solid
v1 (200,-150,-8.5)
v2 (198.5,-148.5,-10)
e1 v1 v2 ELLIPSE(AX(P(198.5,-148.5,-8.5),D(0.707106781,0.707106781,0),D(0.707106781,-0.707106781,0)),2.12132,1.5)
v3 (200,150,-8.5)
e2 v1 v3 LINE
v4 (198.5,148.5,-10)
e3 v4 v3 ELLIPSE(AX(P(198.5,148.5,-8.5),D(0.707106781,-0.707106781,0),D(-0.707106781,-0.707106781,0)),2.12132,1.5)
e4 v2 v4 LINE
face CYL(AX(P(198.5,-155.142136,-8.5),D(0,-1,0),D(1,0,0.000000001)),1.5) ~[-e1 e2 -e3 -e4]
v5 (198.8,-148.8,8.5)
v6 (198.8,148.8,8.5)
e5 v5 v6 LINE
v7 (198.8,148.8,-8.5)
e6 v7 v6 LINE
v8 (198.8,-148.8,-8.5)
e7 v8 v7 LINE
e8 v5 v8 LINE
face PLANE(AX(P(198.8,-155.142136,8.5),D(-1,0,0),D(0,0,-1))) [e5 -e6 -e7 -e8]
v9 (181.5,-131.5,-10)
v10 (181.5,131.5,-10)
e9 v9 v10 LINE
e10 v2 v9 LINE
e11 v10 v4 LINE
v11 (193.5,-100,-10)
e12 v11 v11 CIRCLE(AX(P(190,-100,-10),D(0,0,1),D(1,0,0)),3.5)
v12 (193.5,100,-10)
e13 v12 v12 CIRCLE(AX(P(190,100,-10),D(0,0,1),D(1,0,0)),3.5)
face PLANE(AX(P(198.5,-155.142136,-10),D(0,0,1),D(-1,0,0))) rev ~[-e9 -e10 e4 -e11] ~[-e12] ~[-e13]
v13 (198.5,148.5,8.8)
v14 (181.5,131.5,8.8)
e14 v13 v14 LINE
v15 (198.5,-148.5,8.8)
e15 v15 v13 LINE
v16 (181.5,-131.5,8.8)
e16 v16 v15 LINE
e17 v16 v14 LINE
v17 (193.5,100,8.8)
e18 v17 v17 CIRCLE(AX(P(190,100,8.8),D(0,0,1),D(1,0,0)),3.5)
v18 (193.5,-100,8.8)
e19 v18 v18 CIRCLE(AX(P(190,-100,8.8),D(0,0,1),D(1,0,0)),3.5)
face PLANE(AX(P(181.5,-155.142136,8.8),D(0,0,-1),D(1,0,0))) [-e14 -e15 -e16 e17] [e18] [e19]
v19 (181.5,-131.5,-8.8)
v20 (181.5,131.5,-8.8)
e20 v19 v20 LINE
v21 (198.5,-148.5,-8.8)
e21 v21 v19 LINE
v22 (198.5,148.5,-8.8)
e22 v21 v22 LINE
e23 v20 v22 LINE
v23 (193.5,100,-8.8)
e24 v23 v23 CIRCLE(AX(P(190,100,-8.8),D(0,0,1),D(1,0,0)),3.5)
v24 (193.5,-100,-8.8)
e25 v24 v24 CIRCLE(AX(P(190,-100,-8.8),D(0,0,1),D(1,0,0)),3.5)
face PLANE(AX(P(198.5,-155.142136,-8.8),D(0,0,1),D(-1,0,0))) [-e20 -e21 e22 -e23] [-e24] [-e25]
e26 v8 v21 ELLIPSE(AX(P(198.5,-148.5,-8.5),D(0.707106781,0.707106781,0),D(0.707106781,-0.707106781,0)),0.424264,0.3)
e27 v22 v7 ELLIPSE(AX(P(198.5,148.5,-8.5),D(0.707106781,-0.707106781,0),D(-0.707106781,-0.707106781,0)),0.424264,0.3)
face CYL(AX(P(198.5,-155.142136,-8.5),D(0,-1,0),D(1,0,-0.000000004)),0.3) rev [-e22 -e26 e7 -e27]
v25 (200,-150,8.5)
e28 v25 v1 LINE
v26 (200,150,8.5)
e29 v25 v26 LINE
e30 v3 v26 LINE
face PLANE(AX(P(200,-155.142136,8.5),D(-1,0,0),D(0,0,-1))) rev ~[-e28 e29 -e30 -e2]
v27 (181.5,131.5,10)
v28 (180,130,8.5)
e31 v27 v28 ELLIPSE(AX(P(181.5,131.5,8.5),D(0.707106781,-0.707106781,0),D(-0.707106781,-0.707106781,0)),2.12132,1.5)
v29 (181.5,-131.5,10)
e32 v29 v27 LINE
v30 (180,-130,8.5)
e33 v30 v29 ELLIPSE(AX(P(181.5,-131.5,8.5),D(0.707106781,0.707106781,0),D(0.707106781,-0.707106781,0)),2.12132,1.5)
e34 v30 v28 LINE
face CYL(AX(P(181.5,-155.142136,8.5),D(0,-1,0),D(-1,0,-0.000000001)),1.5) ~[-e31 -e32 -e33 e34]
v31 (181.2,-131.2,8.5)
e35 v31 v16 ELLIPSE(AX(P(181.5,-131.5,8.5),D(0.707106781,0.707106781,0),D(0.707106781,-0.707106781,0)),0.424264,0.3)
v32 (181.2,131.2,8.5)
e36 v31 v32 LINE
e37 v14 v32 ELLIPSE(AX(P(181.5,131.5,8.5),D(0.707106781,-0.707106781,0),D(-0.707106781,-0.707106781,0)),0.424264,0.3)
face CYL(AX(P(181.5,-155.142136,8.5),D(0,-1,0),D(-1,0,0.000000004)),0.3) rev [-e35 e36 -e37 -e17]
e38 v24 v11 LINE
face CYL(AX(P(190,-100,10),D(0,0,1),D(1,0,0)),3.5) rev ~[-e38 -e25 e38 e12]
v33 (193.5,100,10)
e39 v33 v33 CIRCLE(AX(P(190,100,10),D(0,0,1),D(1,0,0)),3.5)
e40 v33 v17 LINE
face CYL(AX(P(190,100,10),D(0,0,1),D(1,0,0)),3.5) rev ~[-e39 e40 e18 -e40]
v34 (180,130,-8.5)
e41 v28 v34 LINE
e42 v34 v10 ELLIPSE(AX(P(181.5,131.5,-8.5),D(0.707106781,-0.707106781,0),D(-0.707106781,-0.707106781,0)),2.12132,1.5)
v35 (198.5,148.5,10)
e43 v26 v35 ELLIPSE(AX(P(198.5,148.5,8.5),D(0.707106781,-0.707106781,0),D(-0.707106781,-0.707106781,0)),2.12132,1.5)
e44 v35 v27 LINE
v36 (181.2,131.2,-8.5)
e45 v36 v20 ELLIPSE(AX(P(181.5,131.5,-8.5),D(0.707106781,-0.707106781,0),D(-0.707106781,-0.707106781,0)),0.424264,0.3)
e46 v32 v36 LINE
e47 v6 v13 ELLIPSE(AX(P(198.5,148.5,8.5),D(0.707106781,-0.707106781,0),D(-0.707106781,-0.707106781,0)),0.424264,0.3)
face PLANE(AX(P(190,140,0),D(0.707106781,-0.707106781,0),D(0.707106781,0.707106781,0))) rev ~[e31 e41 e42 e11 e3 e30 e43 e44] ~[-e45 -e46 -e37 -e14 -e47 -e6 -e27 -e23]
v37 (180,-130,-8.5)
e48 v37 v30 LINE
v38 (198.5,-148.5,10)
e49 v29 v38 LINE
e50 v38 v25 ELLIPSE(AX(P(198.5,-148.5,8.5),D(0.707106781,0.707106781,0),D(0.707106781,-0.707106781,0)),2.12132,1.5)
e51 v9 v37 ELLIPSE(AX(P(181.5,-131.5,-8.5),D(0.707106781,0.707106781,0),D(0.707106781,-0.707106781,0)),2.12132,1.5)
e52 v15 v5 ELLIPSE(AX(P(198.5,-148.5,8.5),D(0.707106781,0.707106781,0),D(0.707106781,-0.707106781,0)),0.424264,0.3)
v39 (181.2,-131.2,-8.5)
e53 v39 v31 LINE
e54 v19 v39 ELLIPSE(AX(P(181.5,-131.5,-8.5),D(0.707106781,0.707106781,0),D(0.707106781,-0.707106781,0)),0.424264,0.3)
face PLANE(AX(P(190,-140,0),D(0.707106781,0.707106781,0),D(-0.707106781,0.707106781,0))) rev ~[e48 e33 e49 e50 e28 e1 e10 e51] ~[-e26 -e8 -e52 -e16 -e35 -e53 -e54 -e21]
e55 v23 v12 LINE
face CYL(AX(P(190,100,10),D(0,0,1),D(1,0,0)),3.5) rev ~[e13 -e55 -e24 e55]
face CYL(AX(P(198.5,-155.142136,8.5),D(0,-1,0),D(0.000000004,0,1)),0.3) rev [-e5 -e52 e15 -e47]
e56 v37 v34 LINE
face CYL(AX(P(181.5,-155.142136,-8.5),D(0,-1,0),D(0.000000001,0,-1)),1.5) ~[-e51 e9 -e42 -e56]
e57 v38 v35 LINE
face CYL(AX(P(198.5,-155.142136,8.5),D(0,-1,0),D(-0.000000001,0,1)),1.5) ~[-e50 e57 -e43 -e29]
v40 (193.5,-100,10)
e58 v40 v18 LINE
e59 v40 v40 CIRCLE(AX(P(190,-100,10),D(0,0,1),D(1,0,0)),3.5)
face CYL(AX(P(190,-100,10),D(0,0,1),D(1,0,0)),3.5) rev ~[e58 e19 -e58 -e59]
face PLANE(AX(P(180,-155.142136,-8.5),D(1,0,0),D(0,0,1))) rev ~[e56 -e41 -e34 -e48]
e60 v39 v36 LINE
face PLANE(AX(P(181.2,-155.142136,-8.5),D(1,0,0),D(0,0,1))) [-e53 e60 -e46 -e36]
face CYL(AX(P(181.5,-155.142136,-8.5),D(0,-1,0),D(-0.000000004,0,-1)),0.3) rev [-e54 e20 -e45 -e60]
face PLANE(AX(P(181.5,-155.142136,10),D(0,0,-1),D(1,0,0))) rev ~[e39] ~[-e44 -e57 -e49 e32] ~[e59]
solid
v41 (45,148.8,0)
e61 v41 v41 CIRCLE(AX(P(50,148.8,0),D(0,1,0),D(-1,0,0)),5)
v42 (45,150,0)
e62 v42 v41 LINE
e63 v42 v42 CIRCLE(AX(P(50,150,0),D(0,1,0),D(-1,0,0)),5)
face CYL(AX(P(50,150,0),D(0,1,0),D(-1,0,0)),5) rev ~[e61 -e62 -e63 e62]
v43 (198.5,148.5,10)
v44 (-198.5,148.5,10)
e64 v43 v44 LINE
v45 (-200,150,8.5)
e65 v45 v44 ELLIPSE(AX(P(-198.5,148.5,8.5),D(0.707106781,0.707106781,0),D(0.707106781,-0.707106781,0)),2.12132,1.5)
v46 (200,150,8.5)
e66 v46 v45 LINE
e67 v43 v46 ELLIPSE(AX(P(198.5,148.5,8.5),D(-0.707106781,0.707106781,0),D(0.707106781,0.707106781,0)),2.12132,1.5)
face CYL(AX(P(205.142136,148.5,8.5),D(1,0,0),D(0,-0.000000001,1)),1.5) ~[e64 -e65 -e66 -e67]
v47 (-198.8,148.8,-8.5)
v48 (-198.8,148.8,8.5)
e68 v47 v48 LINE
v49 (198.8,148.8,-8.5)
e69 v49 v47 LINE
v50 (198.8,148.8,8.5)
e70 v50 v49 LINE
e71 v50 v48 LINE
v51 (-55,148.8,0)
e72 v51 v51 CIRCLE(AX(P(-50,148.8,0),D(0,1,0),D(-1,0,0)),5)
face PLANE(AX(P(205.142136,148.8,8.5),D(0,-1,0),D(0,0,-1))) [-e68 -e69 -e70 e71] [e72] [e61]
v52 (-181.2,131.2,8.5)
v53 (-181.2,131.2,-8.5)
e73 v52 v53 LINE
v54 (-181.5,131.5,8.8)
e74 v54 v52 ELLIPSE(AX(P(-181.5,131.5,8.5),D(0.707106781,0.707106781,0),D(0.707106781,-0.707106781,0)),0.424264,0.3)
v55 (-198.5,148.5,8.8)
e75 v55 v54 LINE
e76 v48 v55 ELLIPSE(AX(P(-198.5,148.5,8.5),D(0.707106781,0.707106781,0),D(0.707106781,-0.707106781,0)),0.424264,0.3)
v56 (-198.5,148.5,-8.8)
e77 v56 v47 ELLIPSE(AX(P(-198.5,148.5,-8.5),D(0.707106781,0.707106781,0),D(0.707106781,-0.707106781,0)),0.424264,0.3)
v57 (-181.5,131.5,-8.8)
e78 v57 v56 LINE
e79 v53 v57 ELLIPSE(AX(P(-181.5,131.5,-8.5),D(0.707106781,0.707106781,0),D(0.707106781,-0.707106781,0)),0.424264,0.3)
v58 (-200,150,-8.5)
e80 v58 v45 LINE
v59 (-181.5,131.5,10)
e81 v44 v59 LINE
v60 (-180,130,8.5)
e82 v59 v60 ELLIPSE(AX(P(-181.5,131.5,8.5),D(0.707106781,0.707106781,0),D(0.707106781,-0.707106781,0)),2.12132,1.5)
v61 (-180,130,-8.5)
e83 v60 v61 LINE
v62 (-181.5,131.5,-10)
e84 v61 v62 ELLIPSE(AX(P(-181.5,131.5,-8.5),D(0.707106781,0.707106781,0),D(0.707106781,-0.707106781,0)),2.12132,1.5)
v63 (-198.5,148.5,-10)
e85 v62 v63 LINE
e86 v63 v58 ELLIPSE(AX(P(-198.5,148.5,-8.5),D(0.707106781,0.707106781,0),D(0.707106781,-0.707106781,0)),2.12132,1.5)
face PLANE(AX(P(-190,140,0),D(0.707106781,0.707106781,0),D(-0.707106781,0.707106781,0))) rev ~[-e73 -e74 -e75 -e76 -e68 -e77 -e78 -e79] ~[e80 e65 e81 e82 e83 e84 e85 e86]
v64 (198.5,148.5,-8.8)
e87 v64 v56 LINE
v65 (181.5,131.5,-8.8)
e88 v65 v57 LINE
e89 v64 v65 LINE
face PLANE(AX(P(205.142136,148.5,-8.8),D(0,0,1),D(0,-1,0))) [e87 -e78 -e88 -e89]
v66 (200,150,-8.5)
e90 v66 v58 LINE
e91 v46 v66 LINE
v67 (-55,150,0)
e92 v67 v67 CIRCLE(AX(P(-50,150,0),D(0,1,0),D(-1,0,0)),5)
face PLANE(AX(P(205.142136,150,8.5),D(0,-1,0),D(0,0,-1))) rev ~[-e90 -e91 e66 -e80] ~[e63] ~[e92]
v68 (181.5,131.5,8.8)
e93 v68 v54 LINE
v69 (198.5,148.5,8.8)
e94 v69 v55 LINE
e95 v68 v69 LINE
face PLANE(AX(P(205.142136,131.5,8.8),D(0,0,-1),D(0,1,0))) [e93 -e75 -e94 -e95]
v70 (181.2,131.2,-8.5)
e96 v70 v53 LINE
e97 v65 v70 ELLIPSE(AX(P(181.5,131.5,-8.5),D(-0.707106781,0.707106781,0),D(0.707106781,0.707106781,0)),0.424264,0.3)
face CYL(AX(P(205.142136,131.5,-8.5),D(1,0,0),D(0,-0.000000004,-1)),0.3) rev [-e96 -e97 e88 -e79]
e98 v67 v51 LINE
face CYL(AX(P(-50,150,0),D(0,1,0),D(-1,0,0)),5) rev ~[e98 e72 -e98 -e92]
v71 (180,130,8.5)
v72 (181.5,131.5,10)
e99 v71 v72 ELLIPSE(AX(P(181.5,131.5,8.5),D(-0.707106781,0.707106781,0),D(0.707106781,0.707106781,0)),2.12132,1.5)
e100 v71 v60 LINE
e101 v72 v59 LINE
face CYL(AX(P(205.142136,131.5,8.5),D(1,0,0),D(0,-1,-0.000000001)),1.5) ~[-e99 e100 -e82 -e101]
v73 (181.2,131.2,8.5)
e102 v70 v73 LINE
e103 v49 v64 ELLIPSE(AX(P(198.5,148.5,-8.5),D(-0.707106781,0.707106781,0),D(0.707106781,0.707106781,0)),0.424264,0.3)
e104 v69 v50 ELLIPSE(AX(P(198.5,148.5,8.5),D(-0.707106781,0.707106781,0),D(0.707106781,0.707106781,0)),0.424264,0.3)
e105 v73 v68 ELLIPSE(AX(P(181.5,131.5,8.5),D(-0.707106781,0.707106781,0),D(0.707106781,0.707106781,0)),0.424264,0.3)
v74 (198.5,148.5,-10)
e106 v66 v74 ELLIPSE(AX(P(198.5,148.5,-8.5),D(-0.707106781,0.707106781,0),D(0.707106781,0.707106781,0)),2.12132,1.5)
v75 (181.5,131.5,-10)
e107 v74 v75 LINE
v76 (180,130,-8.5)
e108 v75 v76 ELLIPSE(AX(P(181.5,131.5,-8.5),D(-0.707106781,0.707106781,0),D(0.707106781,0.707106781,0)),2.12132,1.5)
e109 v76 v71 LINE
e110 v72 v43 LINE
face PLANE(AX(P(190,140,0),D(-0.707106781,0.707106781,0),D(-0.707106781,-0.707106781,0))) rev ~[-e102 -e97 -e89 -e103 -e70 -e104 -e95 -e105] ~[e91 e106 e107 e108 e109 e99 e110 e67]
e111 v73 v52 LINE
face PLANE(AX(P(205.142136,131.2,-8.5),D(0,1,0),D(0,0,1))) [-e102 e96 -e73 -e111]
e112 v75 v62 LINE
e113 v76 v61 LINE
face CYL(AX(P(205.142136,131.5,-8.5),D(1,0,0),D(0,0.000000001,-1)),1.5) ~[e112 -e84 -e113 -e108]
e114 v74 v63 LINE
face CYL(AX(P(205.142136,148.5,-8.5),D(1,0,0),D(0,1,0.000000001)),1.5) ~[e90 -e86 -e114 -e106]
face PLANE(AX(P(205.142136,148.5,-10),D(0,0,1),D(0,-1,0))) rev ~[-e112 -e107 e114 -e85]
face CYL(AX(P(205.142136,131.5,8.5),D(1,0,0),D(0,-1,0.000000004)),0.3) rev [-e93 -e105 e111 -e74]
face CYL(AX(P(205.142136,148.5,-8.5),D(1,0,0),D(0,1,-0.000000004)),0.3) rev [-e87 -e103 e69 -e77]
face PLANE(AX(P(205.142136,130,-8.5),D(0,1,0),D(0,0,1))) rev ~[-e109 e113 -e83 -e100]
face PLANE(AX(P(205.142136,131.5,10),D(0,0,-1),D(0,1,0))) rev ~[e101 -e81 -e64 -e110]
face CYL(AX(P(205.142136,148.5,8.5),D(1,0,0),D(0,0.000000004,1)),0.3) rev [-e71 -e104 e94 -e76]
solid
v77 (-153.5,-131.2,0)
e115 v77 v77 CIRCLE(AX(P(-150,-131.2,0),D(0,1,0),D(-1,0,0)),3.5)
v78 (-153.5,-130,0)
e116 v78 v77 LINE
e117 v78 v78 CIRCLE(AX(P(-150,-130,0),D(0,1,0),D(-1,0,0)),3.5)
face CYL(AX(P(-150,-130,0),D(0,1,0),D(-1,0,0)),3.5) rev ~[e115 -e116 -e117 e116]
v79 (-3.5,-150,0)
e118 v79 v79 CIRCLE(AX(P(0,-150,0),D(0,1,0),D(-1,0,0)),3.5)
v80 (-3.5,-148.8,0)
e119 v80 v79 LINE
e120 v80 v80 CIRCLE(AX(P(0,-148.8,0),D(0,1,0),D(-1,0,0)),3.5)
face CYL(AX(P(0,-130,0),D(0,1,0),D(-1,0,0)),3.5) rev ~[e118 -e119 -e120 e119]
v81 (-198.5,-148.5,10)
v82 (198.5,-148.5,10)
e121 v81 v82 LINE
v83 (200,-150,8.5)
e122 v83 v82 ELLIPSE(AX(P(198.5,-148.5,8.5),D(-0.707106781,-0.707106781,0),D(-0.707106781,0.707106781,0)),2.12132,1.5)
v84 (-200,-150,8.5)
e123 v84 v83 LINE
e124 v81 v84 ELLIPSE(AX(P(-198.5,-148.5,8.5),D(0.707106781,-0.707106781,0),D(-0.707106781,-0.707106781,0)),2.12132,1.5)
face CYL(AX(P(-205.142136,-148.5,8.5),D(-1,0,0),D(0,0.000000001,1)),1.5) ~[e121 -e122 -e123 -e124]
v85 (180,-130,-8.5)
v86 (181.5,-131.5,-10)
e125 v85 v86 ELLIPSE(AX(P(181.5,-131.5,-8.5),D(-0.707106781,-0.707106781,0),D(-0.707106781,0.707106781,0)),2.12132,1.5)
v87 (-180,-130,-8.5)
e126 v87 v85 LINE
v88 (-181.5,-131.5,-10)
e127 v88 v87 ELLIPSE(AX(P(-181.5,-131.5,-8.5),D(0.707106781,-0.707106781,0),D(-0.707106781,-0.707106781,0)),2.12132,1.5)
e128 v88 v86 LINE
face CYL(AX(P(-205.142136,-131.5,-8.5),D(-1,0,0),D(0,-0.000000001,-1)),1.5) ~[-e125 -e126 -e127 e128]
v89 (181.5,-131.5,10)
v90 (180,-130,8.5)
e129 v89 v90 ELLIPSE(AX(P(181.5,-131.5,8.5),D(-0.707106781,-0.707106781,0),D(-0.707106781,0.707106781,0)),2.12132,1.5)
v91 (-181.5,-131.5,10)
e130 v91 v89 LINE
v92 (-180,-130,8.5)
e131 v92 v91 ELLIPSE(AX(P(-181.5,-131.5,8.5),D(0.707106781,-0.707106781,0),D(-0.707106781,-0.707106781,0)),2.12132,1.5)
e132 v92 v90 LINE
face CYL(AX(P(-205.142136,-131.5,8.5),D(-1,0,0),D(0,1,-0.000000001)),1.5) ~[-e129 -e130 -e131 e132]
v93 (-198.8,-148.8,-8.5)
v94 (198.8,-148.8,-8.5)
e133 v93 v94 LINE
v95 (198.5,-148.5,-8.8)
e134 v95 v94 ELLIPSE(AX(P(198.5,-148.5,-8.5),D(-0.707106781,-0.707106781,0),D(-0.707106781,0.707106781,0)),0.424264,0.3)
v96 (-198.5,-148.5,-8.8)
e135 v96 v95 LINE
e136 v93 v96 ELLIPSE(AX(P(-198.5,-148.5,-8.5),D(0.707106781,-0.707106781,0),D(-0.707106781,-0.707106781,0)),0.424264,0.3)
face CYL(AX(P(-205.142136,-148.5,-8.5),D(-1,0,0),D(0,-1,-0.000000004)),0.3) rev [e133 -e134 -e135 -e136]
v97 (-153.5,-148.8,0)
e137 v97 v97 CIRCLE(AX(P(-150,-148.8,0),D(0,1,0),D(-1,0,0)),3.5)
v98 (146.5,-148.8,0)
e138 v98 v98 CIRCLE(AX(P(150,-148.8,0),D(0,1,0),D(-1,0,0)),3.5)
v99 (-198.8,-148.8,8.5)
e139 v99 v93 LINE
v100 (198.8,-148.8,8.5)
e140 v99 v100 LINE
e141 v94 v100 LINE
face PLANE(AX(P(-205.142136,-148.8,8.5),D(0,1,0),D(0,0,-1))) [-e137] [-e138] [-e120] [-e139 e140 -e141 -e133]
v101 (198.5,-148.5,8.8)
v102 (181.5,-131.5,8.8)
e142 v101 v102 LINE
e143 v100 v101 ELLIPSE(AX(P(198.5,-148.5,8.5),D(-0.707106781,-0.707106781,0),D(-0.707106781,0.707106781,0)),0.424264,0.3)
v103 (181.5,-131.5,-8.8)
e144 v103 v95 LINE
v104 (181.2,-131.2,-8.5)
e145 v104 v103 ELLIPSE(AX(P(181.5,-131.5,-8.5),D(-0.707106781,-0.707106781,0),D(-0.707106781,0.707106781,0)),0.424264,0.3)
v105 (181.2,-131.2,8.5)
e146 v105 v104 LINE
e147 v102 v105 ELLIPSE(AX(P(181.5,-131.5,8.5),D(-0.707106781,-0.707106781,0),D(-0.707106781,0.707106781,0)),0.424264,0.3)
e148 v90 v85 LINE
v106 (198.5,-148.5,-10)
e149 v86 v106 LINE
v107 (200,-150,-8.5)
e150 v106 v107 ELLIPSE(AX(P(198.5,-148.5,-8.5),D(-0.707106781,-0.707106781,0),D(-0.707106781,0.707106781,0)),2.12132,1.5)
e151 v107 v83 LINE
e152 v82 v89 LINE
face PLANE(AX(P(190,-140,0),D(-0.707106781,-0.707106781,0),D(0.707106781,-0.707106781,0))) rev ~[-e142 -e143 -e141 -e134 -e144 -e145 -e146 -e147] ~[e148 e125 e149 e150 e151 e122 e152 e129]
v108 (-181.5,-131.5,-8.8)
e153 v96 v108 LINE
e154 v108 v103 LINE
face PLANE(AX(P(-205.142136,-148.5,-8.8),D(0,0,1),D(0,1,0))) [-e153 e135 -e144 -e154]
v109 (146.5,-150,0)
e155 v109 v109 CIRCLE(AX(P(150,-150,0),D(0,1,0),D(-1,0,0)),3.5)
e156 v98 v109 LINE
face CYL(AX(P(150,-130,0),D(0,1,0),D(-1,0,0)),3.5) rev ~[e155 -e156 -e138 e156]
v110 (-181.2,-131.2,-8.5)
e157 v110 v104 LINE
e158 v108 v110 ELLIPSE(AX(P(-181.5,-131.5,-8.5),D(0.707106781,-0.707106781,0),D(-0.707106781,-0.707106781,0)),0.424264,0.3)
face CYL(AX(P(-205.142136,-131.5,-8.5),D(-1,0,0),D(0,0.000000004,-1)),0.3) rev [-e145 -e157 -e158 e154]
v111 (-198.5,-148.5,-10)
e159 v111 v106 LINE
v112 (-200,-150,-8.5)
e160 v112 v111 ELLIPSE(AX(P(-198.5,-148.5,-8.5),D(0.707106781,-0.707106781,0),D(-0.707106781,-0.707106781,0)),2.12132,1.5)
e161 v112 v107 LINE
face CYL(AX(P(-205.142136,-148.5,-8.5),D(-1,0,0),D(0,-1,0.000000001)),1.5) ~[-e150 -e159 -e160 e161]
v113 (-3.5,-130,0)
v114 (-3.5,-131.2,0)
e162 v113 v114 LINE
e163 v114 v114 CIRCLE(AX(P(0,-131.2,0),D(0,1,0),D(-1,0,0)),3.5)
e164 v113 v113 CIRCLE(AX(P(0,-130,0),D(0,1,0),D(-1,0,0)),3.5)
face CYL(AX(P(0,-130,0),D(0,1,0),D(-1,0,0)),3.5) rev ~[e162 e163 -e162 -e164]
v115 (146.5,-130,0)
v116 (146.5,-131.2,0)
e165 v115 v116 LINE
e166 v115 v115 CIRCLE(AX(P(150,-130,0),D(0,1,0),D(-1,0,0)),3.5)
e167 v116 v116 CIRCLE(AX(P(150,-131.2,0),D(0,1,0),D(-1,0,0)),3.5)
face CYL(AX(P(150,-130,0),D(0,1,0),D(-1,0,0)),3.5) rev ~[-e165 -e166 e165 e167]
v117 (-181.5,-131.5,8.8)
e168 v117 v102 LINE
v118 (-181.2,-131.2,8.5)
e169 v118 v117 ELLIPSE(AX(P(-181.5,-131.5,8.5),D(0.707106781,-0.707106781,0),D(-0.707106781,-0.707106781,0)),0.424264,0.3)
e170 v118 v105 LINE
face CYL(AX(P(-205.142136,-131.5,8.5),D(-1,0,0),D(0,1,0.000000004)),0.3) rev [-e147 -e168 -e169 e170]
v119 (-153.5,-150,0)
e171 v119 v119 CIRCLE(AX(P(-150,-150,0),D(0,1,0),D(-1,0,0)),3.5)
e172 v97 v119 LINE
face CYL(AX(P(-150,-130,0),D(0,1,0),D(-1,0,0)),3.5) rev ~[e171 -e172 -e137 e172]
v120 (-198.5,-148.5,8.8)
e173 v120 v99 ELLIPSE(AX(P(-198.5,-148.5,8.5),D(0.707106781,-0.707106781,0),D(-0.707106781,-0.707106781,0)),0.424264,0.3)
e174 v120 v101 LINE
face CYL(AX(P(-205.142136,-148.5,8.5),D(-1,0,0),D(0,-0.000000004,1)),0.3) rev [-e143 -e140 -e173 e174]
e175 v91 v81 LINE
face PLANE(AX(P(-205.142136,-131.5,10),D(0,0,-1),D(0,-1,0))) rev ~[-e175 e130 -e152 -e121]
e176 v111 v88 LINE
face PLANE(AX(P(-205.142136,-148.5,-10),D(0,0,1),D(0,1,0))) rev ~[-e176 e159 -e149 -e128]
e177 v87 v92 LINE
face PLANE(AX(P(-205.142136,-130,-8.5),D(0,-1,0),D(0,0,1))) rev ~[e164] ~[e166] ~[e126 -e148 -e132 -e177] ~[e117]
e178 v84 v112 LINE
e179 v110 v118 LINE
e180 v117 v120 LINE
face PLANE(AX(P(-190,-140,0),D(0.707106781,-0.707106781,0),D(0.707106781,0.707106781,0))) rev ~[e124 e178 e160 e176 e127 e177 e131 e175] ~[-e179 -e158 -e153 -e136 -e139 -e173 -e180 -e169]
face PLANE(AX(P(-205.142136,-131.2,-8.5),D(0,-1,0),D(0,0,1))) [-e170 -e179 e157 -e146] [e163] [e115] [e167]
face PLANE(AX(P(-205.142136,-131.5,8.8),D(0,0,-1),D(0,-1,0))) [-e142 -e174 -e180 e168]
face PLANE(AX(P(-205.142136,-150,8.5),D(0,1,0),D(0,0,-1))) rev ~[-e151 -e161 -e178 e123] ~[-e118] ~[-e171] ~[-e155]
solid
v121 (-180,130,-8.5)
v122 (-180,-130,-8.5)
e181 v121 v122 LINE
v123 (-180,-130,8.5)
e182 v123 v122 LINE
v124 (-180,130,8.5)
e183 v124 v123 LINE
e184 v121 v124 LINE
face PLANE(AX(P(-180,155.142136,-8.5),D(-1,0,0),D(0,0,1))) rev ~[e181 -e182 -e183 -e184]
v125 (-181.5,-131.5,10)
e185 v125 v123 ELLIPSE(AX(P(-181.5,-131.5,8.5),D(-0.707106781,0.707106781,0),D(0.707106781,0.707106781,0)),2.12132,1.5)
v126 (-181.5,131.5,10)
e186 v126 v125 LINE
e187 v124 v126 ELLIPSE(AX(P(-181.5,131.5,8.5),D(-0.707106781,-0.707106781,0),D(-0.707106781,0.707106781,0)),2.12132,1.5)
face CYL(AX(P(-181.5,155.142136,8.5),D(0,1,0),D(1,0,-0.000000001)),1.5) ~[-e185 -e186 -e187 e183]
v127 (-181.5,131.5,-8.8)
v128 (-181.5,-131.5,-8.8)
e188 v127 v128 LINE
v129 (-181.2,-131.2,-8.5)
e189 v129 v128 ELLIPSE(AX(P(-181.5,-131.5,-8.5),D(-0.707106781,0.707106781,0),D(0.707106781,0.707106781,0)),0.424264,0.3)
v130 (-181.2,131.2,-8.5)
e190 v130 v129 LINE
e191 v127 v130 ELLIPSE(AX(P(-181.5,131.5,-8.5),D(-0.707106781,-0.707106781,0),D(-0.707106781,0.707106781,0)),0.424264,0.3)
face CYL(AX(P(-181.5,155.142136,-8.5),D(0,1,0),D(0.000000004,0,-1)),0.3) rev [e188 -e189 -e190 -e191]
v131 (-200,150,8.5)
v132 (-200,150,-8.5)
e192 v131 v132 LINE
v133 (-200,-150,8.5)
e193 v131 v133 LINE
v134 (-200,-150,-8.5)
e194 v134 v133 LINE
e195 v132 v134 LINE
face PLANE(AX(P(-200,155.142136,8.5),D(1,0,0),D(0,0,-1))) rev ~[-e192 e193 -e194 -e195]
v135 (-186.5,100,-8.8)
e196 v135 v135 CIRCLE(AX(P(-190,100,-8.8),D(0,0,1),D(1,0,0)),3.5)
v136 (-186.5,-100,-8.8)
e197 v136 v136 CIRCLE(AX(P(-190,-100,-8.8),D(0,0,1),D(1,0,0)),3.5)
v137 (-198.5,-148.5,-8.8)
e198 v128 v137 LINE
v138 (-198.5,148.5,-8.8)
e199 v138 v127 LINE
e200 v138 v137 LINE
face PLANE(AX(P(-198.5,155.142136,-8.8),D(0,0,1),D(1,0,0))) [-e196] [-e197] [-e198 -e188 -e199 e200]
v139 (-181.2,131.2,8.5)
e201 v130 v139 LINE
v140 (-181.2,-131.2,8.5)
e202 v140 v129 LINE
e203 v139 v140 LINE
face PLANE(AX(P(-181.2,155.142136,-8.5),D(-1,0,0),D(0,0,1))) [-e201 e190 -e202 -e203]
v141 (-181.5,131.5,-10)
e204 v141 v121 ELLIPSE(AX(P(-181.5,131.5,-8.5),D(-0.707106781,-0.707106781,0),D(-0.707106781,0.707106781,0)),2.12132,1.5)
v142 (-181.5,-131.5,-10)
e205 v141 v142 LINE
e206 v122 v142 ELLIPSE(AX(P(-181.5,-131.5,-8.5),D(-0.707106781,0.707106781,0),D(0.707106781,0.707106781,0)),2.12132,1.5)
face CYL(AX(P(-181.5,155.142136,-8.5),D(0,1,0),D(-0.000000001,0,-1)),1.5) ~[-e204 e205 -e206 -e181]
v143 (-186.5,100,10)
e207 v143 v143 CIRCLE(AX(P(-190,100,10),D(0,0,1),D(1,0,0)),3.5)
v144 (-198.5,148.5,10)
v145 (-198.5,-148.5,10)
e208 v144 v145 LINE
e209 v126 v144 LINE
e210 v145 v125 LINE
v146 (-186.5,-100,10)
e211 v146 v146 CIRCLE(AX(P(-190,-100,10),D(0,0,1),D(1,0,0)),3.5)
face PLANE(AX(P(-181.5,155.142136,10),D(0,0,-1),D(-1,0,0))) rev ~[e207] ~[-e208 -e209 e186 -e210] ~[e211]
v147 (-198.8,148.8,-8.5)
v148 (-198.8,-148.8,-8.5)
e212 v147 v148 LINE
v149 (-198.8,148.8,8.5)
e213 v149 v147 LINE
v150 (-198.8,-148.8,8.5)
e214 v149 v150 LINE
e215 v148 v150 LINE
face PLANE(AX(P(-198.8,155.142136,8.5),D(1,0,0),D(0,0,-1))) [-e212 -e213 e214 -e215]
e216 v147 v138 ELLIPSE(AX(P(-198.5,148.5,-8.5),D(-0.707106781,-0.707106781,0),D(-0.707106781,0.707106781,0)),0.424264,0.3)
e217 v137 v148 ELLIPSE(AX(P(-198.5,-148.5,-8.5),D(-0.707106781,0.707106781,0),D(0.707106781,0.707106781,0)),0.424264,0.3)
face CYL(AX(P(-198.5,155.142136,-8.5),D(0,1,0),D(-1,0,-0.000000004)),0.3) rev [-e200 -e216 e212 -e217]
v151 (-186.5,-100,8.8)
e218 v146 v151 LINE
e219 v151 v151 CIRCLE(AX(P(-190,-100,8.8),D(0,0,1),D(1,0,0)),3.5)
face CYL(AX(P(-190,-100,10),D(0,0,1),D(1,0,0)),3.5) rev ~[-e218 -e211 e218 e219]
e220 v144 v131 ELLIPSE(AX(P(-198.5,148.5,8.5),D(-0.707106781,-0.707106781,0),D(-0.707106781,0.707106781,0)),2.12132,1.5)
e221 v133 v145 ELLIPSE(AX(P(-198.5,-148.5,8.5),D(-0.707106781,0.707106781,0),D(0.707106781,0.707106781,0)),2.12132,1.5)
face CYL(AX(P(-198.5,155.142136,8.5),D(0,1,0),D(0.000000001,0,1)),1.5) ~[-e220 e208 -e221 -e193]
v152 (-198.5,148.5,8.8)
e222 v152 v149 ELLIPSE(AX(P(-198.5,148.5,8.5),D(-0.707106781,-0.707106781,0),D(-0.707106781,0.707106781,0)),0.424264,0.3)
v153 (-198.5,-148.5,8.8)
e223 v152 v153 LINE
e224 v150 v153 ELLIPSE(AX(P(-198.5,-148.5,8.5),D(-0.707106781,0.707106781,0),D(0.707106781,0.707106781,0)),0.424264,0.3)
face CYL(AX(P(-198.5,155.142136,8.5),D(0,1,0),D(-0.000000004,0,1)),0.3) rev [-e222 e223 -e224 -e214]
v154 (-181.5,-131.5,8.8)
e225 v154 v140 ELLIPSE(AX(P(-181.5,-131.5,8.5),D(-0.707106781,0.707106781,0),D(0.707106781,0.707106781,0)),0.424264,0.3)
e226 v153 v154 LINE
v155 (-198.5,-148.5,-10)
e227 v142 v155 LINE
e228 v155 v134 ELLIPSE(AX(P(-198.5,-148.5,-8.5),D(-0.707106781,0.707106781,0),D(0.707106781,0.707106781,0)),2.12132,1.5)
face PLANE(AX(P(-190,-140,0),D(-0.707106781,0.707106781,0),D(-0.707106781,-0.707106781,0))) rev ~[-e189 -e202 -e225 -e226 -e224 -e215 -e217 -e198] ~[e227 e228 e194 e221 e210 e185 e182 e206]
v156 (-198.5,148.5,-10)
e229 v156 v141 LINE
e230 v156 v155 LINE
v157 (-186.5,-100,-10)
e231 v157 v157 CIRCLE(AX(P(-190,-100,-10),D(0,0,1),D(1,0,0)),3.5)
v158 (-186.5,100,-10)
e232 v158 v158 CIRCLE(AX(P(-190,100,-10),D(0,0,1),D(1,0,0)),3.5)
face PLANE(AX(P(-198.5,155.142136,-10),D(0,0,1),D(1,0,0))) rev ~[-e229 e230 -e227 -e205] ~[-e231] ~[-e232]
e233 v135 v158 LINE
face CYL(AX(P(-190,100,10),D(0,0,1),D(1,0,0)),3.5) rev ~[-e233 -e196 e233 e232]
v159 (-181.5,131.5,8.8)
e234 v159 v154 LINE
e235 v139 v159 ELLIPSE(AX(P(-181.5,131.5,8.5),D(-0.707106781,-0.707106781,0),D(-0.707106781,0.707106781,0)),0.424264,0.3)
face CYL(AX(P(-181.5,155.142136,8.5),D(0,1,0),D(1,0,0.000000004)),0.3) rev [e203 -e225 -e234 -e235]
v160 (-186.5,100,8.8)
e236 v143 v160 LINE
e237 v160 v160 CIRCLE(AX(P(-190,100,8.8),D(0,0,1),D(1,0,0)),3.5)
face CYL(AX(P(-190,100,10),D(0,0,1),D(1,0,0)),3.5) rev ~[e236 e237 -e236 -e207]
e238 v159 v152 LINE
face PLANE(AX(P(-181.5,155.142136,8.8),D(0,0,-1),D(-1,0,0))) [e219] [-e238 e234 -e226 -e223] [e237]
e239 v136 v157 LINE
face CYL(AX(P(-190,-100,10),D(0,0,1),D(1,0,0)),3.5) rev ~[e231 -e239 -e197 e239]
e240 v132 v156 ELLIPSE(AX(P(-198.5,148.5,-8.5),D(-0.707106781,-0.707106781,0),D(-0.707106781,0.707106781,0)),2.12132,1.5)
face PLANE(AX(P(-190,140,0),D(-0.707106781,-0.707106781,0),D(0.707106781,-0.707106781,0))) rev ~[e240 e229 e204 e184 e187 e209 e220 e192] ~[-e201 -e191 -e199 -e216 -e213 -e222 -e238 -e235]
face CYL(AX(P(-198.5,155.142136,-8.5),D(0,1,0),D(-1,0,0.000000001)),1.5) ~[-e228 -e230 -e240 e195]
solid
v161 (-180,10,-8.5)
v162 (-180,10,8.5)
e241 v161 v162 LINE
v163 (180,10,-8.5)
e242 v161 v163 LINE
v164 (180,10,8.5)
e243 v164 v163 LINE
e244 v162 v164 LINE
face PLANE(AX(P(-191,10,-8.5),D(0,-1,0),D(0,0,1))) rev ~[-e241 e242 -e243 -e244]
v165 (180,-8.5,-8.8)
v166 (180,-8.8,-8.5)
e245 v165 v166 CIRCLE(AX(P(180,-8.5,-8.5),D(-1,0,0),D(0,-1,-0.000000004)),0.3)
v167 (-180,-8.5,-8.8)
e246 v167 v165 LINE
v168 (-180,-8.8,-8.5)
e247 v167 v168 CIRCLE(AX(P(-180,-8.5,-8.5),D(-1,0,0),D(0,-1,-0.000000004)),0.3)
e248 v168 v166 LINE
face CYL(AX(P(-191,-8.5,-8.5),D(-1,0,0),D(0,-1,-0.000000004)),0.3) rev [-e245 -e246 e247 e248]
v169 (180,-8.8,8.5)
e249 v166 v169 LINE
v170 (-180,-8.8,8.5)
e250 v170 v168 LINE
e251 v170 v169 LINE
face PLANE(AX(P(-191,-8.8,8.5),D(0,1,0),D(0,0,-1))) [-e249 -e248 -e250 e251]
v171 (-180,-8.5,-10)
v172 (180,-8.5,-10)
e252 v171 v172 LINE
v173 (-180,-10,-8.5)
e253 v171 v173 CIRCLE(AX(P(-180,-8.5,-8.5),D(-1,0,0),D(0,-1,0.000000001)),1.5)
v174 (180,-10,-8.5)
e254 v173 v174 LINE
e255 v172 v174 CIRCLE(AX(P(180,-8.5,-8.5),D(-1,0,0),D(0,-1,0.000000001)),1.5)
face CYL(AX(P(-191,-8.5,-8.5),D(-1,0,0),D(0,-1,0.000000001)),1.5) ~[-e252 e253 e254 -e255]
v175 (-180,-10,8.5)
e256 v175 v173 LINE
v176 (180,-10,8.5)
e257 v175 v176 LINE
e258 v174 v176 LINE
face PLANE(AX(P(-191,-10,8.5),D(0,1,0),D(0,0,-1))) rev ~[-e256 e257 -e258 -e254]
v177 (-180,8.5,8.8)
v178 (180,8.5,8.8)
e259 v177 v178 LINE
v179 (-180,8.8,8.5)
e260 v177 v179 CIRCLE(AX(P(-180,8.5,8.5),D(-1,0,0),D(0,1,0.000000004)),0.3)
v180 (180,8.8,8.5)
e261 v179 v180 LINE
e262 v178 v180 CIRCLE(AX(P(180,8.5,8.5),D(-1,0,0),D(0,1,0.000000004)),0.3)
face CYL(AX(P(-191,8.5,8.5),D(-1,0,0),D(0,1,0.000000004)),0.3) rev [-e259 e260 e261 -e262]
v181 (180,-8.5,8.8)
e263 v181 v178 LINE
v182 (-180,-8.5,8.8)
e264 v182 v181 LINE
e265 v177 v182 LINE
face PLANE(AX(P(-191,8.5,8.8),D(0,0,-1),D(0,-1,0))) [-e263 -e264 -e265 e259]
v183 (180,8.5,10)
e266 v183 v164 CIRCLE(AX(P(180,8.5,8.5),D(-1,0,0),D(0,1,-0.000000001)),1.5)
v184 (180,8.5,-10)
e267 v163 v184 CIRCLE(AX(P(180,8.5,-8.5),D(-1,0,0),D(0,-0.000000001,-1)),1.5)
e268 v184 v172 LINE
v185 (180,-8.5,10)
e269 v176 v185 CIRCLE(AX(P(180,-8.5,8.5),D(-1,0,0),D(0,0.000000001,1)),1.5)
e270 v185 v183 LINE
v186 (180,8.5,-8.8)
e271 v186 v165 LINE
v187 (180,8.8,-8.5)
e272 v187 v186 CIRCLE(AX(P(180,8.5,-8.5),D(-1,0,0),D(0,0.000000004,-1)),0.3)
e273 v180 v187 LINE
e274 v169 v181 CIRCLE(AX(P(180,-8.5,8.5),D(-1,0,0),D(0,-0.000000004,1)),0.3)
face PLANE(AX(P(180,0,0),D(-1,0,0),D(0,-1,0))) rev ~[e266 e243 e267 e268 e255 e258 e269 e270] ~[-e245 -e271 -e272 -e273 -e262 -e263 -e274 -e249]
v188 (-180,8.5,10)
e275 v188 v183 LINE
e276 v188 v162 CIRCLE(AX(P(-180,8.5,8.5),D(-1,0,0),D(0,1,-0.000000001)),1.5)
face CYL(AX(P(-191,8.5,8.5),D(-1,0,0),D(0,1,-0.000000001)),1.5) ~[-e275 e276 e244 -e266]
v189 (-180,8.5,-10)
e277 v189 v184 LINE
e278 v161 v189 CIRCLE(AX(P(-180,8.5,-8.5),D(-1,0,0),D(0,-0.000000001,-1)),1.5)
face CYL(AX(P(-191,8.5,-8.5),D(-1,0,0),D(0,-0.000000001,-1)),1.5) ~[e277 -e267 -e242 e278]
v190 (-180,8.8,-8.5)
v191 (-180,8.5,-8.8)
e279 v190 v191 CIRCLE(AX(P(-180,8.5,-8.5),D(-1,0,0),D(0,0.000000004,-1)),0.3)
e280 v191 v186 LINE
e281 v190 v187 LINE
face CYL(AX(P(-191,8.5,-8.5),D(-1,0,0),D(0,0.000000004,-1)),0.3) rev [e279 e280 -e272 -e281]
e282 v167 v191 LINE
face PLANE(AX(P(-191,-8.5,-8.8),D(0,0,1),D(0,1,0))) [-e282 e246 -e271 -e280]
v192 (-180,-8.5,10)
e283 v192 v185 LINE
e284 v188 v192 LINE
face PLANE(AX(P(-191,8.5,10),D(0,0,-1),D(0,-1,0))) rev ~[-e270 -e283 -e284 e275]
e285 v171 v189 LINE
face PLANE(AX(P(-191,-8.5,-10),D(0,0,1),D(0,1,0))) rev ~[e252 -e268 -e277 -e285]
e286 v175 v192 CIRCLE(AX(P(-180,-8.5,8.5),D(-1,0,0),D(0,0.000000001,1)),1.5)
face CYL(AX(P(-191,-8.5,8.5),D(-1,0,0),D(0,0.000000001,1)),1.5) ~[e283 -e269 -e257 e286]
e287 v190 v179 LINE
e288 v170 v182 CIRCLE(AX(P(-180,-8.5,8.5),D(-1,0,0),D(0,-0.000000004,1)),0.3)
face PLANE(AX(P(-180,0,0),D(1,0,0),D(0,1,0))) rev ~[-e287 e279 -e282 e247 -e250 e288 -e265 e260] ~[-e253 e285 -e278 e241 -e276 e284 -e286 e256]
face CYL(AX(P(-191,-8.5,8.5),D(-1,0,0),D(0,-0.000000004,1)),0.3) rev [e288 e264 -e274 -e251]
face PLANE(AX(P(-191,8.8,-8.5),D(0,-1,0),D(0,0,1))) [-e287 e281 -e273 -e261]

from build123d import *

# Parameters (mm, degrees)
STRUCTURAL_MEMBER1_DEPTH      = 395.142135624
STRUCTURAL_MEMBER1_DEPTH_BACK = 15.142135624
STRUCTURAL_MEMBER1_2_DEPTH    = 310.284271247
STRUCTURAL_MEMBER1_3_DEPTH    = 410.284271247
STRUCTURAL_MEMBER1_4_DEPTH    = 310.284271247
STRUCTURAL_MEMBER1_5_DEPTH    = 382
SKETCH3_R                     = 3.5
CUT_EXTRUDE1_DEPTH            = 251.79872408
SKETCH4_R                     = 5
CUT_EXTRUDE2_DEPTH            = 10
SKETCH5_R                     = 3.5
CUT_EXTRUDE3_DEPTH            = 20


with BuildPart() as part:
    # Sketch1 → Structural Member1 (new, two sides: drawn at the far end of the back side and taken through both)
    with BuildSketch(Plane(origin=(190, 140, 0), x_dir=(0, -1, 0), z_dir=(-1, 0, 0)).offset(-STRUCTURAL_MEMBER1_DEPTH_BACK)):
        with BuildLine():
            Line((-8.5, -10), (8.5, -10))
            ThreePointArc((8.5, -10), (9.560660172, -9.560660172), (10, -8.5))
            Line((10, -8.5), (10, 8.5))
            ThreePointArc((10, 8.5), (9.560660172, 9.560660172), (8.5, 10))
            Line((8.5, 10), (-8.5, 10))
            ThreePointArc((-8.5, 10), (-9.560660172, 9.560660172), (-10, 8.5))
            Line((-10, 8.5), (-10, -8.5))
            ThreePointArc((-10, -8.5), (-9.560660172, -9.560660172), (-8.5, -10))
        make_face()
        with BuildLine():
            Line((-8.5, -8.8), (8.5, -8.8))
            ThreePointArc((8.5, -8.8), (8.712132034, -8.712132034), (8.8, -8.5))
            Line((8.8, -8.5), (8.8, 8.5))
            ThreePointArc((8.8, 8.5), (8.712132034, 8.712132034), (8.5, 8.8))
            Line((8.5, 8.8), (-8.5, 8.8))
            ThreePointArc((-8.5, 8.8), (-8.712132034, 8.712132034), (-8.8, 8.5))
            Line((-8.8, 8.5), (-8.8, -8.5))
            ThreePointArc((-8.8, -8.5), (-8.712132034, -8.712132034), (-8.5, -8.8))
        make_face(mode=Mode.SUBTRACT)
    extrude(amount=STRUCTURAL_MEMBER1_DEPTH + STRUCTURAL_MEMBER1_DEPTH_BACK)

    # Structural Member1 mitre 1
    split(bisect_by=Plane(origin=(190, 140, 0), x_dir=(-0.707106781, -0.707106781, 0), z_dir=(-0.707106781, 0.707106781, 0)), keep=Keep.TOP)

    # Structural Member1 mitre 2
    split(bisect_by=Plane(origin=(-190, 140, 0), x_dir=(-0.707106781, 0.707106781, 0), z_dir=(0.707106781, 0.707106781, 0)), keep=Keep.TOP)

    # Sketch4 → Cut-Extrude2 (cut)
    with BuildSketch(Plane(origin=(0, 150, 0), x_dir=(-1, 0, 0), z_dir=(0, 1, 0))):
        with Locations((50, 0)):
            Circle(SKETCH4_R)
        with Locations((-50, 0)):
            Circle(SKETCH4_R)
    extrude(amount=-CUT_EXTRUDE2_DEPTH, mode=Mode.SUBTRACT)


with BuildPart() as body_2:
    # Sketch1 on segment 2 (carried to segment 2) → Structural Member1 2 (new body)
    with BuildSketch(Plane(origin=(-190, 155.142135624, 0), x_dir=(1, 0, 0), z_dir=(0, -1, 0))):
        with BuildLine():
            Line((-8.5, -10), (8.5, -10))
            ThreePointArc((8.5, -10), (9.560660172, -9.560660172), (10, -8.5))
            Line((10, -8.5), (10, 8.5))
            ThreePointArc((10, 8.5), (9.560660172, 9.560660172), (8.5, 10))
            Line((8.5, 10), (-8.5, 10))
            ThreePointArc((-8.5, 10), (-9.560660172, 9.560660172), (-10, 8.5))
            Line((-10, 8.5), (-10, -8.5))
            ThreePointArc((-10, -8.5), (-9.560660172, -9.560660172), (-8.5, -10))
        make_face()
        with BuildLine():
            Line((-8.5, -8.8), (8.5, -8.8))
            ThreePointArc((8.5, -8.8), (8.712132034, -8.712132034), (8.8, -8.5))
            Line((8.8, -8.5), (8.8, 8.5))
            ThreePointArc((8.8, 8.5), (8.712132034, 8.712132034), (8.5, 8.8))
            Line((8.5, 8.8), (-8.5, 8.8))
            ThreePointArc((-8.5, 8.8), (-8.712132034, 8.712132034), (-8.8, 8.5))
            Line((-8.8, 8.5), (-8.8, -8.5))
            ThreePointArc((-8.8, -8.5), (-8.712132034, -8.712132034), (-8.5, -8.8))
        make_face(mode=Mode.SUBTRACT)
    extrude(amount=STRUCTURAL_MEMBER1_2_DEPTH)

    # Structural Member1 2 mitre 1
    split(bisect_by=Plane(origin=(-190, 140, 0), x_dir=(0.707106781, -0.707106781, 0), z_dir=(-0.707106781, -0.707106781, 0)), keep=Keep.TOP)

    # Structural Member1 2 mitre 2
    split(bisect_by=Plane(origin=(-190, -140, 0), x_dir=(-0.707106781, -0.707106781, 0), z_dir=(-0.707106781, 0.707106781, 0)), keep=Keep.TOP)


with BuildPart() as body_3:
    # Sketch1 on segment 3 (carried to segment 3) → Structural Member1 3 (new body)
    with BuildSketch(Plane(origin=(-205.142135624, -140, 0), x_dir=(0, 1, 0), z_dir=(1, 0, 0))):
        with BuildLine():
            Line((-8.5, -10), (8.5, -10))
            ThreePointArc((8.5, -10), (9.560660172, -9.560660172), (10, -8.5))
            Line((10, -8.5), (10, 8.5))
            ThreePointArc((10, 8.5), (9.560660172, 9.560660172), (8.5, 10))
            Line((8.5, 10), (-8.5, 10))
            ThreePointArc((-8.5, 10), (-9.560660172, 9.560660172), (-10, 8.5))
            Line((-10, 8.5), (-10, -8.5))
            ThreePointArc((-10, -8.5), (-9.560660172, -9.560660172), (-8.5, -10))
        make_face()
        with BuildLine():
            Line((-8.5, -8.8), (8.5, -8.8))
            ThreePointArc((8.5, -8.8), (8.712132034, -8.712132034), (8.8, -8.5))
            Line((8.8, -8.5), (8.8, 8.5))
            ThreePointArc((8.8, 8.5), (8.712132034, 8.712132034), (8.5, 8.8))
            Line((8.5, 8.8), (-8.5, 8.8))
            ThreePointArc((-8.5, 8.8), (-8.712132034, 8.712132034), (-8.8, 8.5))
            Line((-8.8, 8.5), (-8.8, -8.5))
            ThreePointArc((-8.8, -8.5), (-8.712132034, -8.712132034), (-8.5, -8.8))
        make_face(mode=Mode.SUBTRACT)
    extrude(amount=STRUCTURAL_MEMBER1_3_DEPTH)

    # Structural Member1 3 mitre 1
    split(bisect_by=Plane(origin=(190, -140, 0), x_dir=(0.707106781, -0.707106781, 0), z_dir=(-0.707106781, -0.707106781, 0)), keep=Keep.TOP)

    # Structural Member1 3 mitre 2
    split(bisect_by=Plane(origin=(-190, -140, 0), x_dir=(0.707106781, 0.707106781, 0), z_dir=(0.707106781, -0.707106781, 0)), keep=Keep.TOP)

    # Sketch5 → Cut-Extrude3 (cut)
    with BuildSketch(Plane(origin=(0, -130, 0), x_dir=(-1, 0, 0), z_dir=(0, 1, 0))):
        Circle(SKETCH5_R)
        with Locations((-150, 0)):
            Circle(SKETCH5_R)
        with Locations((150, 0)):
            Circle(SKETCH5_R)
    extrude(amount=-CUT_EXTRUDE3_DEPTH, mode=Mode.SUBTRACT)


with BuildPart() as body_4:
    # Sketch1 on segment 4 (carried to segment 4) → Structural Member1 4 (new body)
    with BuildSketch(Plane(origin=(190, -155.142135624, 0), x_dir=(-1, 0, 0), z_dir=(0, 1, 0))):
        with BuildLine():
            Line((-8.5, -10), (8.5, -10))
            ThreePointArc((8.5, -10), (9.560660172, -9.560660172), (10, -8.5))
            Line((10, -8.5), (10, 8.5))
            ThreePointArc((10, 8.5), (9.560660172, 9.560660172), (8.5, 10))
            Line((8.5, 10), (-8.5, 10))
            ThreePointArc((-8.5, 10), (-9.560660172, 9.560660172), (-10, 8.5))
            Line((-10, 8.5), (-10, -8.5))
            ThreePointArc((-10, -8.5), (-9.560660172, -9.560660172), (-8.5, -10))
        make_face()
        with BuildLine():
            Line((-8.5, -8.8), (8.5, -8.8))
            ThreePointArc((8.5, -8.8), (8.712132034, -8.712132034), (8.8, -8.5))
            Line((8.8, -8.5), (8.8, 8.5))
            ThreePointArc((8.8, 8.5), (8.712132034, 8.712132034), (8.5, 8.8))
            Line((8.5, 8.8), (-8.5, 8.8))
            ThreePointArc((-8.5, 8.8), (-8.712132034, 8.712132034), (-8.8, 8.5))
            Line((-8.8, 8.5), (-8.8, -8.5))
            ThreePointArc((-8.8, -8.5), (-8.712132034, -8.712132034), (-8.5, -8.8))
        make_face(mode=Mode.SUBTRACT)
    extrude(amount=STRUCTURAL_MEMBER1_4_DEPTH)

    # Structural Member1 4 mitre 1
    split(bisect_by=Plane(origin=(190, 140, 0), x_dir=(0.707106781, 0.707106781, 0), z_dir=(0.707106781, -0.707106781, 0)), keep=Keep.TOP)

    # Structural Member1 4 mitre 2
    split(bisect_by=Plane(origin=(190, -140, 0), x_dir=(-0.707106781, 0.707106781, 0), z_dir=(0.707106781, 0.707106781, 0)), keep=Keep.TOP)


with BuildPart() as body_5:
    # Sketch1 on segment 5 (carried to segment 5) → Structural Member1 5 (new body)
    with BuildSketch(Plane.YZ.offset(-191)):
        with BuildLine():
            Line((-8.5, -10), (8.5, -10))
            ThreePointArc((8.5, -10), (9.560660172, -9.560660172), (10, -8.5))
            Line((10, -8.5), (10, 8.5))
            ThreePointArc((10, 8.5), (9.560660172, 9.560660172), (8.5, 10))
            Line((8.5, 10), (-8.5, 10))
            ThreePointArc((-8.5, 10), (-9.560660172, 9.560660172), (-10, 8.5))
            Line((-10, 8.5), (-10, -8.5))
            ThreePointArc((-10, -8.5), (-9.560660172, -9.560660172), (-8.5, -10))
        make_face()
        with BuildLine():
            Line((-8.5, -8.8), (8.5, -8.8))
            ThreePointArc((8.5, -8.8), (8.712132034, -8.712132034), (8.8, -8.5))
            Line((8.8, -8.5), (8.8, 8.5))
            ThreePointArc((8.8, 8.5), (8.712132034, 8.712132034), (8.5, 8.8))
            Line((8.5, 8.8), (-8.5, 8.8))
            ThreePointArc((-8.5, 8.8), (-8.712132034, 8.712132034), (-8.8, 8.5))
            Line((-8.8, 8.5), (-8.8, -8.5))
            ThreePointArc((-8.8, -8.5), (-8.712132034, -8.712132034), (-8.5, -8.8))
        make_face(mode=Mode.SUBTRACT)
    extrude(amount=STRUCTURAL_MEMBER1_5_DEPTH)

    # Structural Member1 5 mitre 1
    split(bisect_by=Plane.YZ.offset(-180), keep=Keep.TOP)

    # Structural Member1 5 mitre 2
    split(bisect_by=Plane(origin=(180, 0, 0), x_dir=(0, -1, 0), z_dir=(-1, 0, 0)), keep=Keep.TOP)


with BuildPart() as cut_extrude1_tool:
    # Sketch3 → Cut-Extrude1 (new, through all)
    with BuildSketch(Plane.XY.offset(10)):
        with Locations((-190, 100)):
            Circle(SKETCH3_R)
        with Locations((-190, -100)):
            Circle(SKETCH3_R)
        with Locations((190, -100)):
            Circle(SKETCH3_R)
        with Locations((190, 100)):
            Circle(SKETCH3_R)
    extrude(amount=-CUT_EXTRUDE1_DEPTH)


with BuildPart() as body_2_1:
    add(body_2.part)

    # Cut-Extrude1: cut by cut_extrude1_tool
    add(cut_extrude1_tool.part, mode=Mode.SUBTRACT)


with BuildPart() as body_4_1:
    add(body_4.part)

    # Cut-Extrude1: cut by cut_extrude1_tool
    add(cut_extrude1_tool.part, mode=Mode.SUBTRACT)


solid = Compound([part.part, body_3.part, body_5.part, body_2_1.part, body_4_1.part])
